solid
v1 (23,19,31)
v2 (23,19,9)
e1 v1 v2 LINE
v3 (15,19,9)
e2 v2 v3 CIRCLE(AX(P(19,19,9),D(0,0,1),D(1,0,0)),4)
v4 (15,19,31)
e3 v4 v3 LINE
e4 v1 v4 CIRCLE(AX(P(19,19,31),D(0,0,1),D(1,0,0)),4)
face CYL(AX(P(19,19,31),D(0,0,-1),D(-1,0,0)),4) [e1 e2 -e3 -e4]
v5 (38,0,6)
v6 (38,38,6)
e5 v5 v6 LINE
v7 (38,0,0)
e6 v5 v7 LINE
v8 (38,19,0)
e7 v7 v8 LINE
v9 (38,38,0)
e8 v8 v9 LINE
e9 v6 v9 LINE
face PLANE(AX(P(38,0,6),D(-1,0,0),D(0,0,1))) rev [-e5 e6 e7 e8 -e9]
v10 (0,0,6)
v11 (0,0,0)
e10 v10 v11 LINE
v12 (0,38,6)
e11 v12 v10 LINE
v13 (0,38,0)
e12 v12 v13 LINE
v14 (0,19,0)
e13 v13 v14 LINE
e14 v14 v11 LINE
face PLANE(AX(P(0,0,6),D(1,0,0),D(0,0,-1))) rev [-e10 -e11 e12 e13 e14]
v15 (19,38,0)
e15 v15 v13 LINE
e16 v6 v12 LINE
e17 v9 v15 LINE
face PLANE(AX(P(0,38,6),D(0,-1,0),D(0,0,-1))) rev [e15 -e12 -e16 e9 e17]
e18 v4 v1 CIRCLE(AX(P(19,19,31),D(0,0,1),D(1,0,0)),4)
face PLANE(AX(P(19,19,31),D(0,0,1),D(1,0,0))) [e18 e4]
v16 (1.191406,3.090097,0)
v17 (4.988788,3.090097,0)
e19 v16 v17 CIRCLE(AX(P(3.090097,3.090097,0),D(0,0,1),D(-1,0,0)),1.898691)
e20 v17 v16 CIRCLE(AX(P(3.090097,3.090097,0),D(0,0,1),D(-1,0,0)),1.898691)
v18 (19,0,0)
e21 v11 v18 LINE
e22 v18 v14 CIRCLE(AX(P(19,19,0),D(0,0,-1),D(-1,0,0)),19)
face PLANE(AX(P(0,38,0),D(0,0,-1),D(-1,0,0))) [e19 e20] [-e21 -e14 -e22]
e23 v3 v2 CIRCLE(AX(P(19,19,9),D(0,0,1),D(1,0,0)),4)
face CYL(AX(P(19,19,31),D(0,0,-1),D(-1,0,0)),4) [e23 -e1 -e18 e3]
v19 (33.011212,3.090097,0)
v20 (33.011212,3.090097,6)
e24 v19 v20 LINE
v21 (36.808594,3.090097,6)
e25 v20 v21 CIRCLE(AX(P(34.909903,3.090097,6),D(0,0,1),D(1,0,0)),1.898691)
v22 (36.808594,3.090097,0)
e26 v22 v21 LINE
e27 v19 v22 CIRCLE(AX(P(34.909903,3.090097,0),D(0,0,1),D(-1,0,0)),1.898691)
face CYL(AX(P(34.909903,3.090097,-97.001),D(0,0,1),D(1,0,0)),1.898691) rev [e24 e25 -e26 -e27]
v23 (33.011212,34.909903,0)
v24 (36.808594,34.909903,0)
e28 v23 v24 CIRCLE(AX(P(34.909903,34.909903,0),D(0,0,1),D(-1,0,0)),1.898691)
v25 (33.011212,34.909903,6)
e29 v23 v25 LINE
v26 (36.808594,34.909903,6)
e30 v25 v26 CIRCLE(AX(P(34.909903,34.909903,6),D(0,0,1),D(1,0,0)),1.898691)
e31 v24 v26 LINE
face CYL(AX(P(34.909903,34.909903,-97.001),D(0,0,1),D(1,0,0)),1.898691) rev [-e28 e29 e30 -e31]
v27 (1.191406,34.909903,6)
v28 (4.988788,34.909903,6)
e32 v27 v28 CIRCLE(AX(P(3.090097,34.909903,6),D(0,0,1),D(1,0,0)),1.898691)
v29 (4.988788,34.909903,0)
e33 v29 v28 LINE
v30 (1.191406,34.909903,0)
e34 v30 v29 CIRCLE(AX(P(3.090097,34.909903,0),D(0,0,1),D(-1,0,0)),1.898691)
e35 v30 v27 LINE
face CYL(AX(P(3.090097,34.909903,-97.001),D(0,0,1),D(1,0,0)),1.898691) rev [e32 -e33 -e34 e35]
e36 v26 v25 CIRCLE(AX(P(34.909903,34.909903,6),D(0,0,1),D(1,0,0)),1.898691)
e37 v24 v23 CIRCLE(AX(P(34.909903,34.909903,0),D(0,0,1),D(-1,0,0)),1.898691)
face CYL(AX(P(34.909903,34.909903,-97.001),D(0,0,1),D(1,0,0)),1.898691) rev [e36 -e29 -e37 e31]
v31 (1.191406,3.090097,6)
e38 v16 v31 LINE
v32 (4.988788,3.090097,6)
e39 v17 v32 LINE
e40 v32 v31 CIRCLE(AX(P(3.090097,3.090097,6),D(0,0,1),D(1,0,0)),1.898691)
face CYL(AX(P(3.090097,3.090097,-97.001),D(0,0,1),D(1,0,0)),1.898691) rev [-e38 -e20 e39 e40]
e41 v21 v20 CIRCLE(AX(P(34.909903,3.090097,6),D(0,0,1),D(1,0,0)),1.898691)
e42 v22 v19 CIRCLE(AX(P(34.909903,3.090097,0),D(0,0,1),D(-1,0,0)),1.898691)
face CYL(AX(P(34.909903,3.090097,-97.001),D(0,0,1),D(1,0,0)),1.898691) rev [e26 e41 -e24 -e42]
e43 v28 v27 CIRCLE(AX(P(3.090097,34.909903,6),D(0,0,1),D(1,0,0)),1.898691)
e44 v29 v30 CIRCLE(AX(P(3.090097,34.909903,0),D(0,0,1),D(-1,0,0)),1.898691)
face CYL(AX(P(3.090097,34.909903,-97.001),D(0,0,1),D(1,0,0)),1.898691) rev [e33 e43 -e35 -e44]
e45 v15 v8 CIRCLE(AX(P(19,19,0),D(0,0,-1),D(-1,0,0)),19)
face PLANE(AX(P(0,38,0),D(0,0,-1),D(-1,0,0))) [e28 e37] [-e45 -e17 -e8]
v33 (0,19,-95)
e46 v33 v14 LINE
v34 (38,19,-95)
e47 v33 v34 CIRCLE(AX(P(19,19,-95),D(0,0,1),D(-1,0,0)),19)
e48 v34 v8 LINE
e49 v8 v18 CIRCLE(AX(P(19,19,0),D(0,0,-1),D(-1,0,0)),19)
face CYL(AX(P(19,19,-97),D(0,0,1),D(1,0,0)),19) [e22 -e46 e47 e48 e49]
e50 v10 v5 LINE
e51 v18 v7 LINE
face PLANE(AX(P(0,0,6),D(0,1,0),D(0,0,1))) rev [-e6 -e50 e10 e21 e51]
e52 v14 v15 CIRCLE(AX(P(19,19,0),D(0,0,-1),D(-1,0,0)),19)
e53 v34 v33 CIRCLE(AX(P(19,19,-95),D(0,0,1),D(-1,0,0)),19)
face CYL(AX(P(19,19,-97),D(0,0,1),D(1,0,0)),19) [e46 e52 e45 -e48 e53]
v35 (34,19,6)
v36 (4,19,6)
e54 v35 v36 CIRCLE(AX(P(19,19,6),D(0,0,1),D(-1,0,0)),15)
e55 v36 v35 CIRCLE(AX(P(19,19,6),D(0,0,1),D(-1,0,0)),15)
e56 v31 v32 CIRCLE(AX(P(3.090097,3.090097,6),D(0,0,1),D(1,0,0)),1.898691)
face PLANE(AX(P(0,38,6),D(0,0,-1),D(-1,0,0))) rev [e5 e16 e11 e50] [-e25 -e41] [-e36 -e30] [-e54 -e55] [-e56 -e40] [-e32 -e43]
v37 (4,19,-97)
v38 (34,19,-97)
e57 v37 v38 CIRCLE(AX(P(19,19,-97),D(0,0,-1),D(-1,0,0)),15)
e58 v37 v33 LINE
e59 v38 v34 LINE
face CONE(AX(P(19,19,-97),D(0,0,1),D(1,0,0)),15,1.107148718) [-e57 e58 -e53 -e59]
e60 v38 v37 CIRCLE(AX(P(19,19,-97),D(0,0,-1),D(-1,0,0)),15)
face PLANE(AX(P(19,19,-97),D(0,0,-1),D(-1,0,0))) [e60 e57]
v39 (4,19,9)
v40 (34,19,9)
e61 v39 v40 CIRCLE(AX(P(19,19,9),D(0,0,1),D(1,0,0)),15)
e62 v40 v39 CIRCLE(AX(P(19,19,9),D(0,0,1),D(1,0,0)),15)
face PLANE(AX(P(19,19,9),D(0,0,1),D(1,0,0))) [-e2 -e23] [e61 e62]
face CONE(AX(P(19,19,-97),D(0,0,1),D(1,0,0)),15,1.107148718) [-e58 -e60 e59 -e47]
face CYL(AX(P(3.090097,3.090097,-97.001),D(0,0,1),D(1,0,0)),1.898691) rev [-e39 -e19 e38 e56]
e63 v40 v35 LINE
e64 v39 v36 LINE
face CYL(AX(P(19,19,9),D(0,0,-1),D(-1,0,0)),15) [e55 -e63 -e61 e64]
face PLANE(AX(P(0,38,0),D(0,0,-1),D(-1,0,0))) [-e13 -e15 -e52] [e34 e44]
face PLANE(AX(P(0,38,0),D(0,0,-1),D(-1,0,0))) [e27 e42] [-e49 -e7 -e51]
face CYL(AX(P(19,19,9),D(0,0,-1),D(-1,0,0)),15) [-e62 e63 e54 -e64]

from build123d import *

# Parameters (mm, degrees)
SKETCH_1_W          = 38
SKETCH_1_H          = 38
EXTRUDE_1_DEPTH     = 6
SKETCH_2_R          = 15
EXTRUDE_2_DEPTH     = 3
SKETCH_3_R          = 4
EXTRUDE_3_DEPTH     = 22
SKETCH_4_R          = 19
EXTRUDE_4_DEPTH     = 97
CUT_EXTRUDE_1_REACH = 118.177
SKETCH_5_R          = 1.898690993
CHAMFER_1_SIZE      = 2
CHAMFER_1_SIZE2     = 4


with BuildPart() as part:
    # 草图1 → 拉伸1 (new body)
    with BuildSketch(Plane.XY):
        with Locations((19, 19)):
            Rectangle(SKETCH_1_W, SKETCH_1_H)
    extrude(amount=EXTRUDE_1_DEPTH)

    # 草图2 → 拉伸2 (add)
    with BuildSketch(Plane.XY.offset(6)):
        with Locations(Location((19, 19, 0), (0, 0, 180))):
            Circle(SKETCH_2_R)
    extrude(amount=EXTRUDE_2_DEPTH)

    # 草图3 → 拉伸3 (add)
    with BuildSketch(Plane.XY.offset(9)):
        with Locations((19, 19)):
            Circle(SKETCH_3_R)
    extrude(amount=EXTRUDE_3_DEPTH)

    # 草图4 → 拉伸4 (add)
    with BuildSketch(Plane(origin=(0, 0, 0), x_dir=(-1, 0, 0), z_dir=(0, 0, -1))):
        with Locations((-19, 19)):
            Circle(SKETCH_4_R)
    extrude(amount=EXTRUDE_4_DEPTH)

    # 草图5 → 切除-拉伸1 (cut, up to next)
    with BuildSketch(Plane.XY.offset(6), mode=Mode.PRIVATE) as cut_extrude_1_sk1:
        with Locations((3.090097423, 34.909902577)):
            Circle(SKETCH_5_R)
    cut_extrude_1_tool1 = extrude(cut_extrude_1_sk1.sketch, amount=-CUT_EXTRUDE_1_REACH, mode=Mode.PRIVATE) & part.part
    # 草图5 → 切除-拉伸1 (cut, up to next)
    with BuildSketch(Plane.XY.offset(6), mode=Mode.PRIVATE) as cut_extrude_1_sk2:
        with Locations((34.909902577, 34.909902577)):
            Circle(SKETCH_5_R)
    cut_extrude_1_tool2 = extrude(cut_extrude_1_sk2.sketch, amount=-CUT_EXTRUDE_1_REACH, mode=Mode.PRIVATE) & part.part
    # 草图5 → 切除-拉伸1 (cut, up to next)
    with BuildSketch(Plane.XY.offset(6), mode=Mode.PRIVATE) as cut_extrude_1_sk3:
        with Locations((34.909902577, 3.090097423)):
            Circle(SKETCH_5_R)
    cut_extrude_1_tool3 = extrude(cut_extrude_1_sk3.sketch, amount=-CUT_EXTRUDE_1_REACH, mode=Mode.PRIVATE) & part.part
    # 草图5 → 切除-拉伸1 (cut, up to next)
    with BuildSketch(Plane.XY.offset(6), mode=Mode.PRIVATE) as cut_extrude_1_sk4:
        with Locations((3.090097423, 3.090097423)):
            Circle(SKETCH_5_R)
    cut_extrude_1_tool4 = extrude(cut_extrude_1_sk4.sketch, amount=-CUT_EXTRUDE_1_REACH, mode=Mode.PRIVATE) & part.part
    add(cut_extrude_1_tool1.solids().sort_by_distance((3.090097, 34.909903, 6))[0], mode=Mode.SUBTRACT)
    add(cut_extrude_1_tool2.solids().sort_by_distance((34.909903, 34.909903, 6))[0], mode=Mode.SUBTRACT)
    add(cut_extrude_1_tool3.solids().sort_by_distance((34.909903, 3.090097, 6))[0], mode=Mode.SUBTRACT)
    add(cut_extrude_1_tool4.solids().sort_by_distance((3.090097, 3.090097, 6))[0], mode=Mode.SUBTRACT)

    # 倒角1
    chamfer_1_edges = [part.edges().sort_by_distance(p)[0] for p in [
        (38, 19, -97),
    ]]
    chamfer_1_side = [part.faces().sort_by_distance(p)[0] for p in [
        (38, 19, -48.5),
    ]]
    chamfer(chamfer_1_edges, length=CHAMFER_1_SIZE, length2=CHAMFER_1_SIZE2, reference=chamfer_1_side[0])


solid = part.part
